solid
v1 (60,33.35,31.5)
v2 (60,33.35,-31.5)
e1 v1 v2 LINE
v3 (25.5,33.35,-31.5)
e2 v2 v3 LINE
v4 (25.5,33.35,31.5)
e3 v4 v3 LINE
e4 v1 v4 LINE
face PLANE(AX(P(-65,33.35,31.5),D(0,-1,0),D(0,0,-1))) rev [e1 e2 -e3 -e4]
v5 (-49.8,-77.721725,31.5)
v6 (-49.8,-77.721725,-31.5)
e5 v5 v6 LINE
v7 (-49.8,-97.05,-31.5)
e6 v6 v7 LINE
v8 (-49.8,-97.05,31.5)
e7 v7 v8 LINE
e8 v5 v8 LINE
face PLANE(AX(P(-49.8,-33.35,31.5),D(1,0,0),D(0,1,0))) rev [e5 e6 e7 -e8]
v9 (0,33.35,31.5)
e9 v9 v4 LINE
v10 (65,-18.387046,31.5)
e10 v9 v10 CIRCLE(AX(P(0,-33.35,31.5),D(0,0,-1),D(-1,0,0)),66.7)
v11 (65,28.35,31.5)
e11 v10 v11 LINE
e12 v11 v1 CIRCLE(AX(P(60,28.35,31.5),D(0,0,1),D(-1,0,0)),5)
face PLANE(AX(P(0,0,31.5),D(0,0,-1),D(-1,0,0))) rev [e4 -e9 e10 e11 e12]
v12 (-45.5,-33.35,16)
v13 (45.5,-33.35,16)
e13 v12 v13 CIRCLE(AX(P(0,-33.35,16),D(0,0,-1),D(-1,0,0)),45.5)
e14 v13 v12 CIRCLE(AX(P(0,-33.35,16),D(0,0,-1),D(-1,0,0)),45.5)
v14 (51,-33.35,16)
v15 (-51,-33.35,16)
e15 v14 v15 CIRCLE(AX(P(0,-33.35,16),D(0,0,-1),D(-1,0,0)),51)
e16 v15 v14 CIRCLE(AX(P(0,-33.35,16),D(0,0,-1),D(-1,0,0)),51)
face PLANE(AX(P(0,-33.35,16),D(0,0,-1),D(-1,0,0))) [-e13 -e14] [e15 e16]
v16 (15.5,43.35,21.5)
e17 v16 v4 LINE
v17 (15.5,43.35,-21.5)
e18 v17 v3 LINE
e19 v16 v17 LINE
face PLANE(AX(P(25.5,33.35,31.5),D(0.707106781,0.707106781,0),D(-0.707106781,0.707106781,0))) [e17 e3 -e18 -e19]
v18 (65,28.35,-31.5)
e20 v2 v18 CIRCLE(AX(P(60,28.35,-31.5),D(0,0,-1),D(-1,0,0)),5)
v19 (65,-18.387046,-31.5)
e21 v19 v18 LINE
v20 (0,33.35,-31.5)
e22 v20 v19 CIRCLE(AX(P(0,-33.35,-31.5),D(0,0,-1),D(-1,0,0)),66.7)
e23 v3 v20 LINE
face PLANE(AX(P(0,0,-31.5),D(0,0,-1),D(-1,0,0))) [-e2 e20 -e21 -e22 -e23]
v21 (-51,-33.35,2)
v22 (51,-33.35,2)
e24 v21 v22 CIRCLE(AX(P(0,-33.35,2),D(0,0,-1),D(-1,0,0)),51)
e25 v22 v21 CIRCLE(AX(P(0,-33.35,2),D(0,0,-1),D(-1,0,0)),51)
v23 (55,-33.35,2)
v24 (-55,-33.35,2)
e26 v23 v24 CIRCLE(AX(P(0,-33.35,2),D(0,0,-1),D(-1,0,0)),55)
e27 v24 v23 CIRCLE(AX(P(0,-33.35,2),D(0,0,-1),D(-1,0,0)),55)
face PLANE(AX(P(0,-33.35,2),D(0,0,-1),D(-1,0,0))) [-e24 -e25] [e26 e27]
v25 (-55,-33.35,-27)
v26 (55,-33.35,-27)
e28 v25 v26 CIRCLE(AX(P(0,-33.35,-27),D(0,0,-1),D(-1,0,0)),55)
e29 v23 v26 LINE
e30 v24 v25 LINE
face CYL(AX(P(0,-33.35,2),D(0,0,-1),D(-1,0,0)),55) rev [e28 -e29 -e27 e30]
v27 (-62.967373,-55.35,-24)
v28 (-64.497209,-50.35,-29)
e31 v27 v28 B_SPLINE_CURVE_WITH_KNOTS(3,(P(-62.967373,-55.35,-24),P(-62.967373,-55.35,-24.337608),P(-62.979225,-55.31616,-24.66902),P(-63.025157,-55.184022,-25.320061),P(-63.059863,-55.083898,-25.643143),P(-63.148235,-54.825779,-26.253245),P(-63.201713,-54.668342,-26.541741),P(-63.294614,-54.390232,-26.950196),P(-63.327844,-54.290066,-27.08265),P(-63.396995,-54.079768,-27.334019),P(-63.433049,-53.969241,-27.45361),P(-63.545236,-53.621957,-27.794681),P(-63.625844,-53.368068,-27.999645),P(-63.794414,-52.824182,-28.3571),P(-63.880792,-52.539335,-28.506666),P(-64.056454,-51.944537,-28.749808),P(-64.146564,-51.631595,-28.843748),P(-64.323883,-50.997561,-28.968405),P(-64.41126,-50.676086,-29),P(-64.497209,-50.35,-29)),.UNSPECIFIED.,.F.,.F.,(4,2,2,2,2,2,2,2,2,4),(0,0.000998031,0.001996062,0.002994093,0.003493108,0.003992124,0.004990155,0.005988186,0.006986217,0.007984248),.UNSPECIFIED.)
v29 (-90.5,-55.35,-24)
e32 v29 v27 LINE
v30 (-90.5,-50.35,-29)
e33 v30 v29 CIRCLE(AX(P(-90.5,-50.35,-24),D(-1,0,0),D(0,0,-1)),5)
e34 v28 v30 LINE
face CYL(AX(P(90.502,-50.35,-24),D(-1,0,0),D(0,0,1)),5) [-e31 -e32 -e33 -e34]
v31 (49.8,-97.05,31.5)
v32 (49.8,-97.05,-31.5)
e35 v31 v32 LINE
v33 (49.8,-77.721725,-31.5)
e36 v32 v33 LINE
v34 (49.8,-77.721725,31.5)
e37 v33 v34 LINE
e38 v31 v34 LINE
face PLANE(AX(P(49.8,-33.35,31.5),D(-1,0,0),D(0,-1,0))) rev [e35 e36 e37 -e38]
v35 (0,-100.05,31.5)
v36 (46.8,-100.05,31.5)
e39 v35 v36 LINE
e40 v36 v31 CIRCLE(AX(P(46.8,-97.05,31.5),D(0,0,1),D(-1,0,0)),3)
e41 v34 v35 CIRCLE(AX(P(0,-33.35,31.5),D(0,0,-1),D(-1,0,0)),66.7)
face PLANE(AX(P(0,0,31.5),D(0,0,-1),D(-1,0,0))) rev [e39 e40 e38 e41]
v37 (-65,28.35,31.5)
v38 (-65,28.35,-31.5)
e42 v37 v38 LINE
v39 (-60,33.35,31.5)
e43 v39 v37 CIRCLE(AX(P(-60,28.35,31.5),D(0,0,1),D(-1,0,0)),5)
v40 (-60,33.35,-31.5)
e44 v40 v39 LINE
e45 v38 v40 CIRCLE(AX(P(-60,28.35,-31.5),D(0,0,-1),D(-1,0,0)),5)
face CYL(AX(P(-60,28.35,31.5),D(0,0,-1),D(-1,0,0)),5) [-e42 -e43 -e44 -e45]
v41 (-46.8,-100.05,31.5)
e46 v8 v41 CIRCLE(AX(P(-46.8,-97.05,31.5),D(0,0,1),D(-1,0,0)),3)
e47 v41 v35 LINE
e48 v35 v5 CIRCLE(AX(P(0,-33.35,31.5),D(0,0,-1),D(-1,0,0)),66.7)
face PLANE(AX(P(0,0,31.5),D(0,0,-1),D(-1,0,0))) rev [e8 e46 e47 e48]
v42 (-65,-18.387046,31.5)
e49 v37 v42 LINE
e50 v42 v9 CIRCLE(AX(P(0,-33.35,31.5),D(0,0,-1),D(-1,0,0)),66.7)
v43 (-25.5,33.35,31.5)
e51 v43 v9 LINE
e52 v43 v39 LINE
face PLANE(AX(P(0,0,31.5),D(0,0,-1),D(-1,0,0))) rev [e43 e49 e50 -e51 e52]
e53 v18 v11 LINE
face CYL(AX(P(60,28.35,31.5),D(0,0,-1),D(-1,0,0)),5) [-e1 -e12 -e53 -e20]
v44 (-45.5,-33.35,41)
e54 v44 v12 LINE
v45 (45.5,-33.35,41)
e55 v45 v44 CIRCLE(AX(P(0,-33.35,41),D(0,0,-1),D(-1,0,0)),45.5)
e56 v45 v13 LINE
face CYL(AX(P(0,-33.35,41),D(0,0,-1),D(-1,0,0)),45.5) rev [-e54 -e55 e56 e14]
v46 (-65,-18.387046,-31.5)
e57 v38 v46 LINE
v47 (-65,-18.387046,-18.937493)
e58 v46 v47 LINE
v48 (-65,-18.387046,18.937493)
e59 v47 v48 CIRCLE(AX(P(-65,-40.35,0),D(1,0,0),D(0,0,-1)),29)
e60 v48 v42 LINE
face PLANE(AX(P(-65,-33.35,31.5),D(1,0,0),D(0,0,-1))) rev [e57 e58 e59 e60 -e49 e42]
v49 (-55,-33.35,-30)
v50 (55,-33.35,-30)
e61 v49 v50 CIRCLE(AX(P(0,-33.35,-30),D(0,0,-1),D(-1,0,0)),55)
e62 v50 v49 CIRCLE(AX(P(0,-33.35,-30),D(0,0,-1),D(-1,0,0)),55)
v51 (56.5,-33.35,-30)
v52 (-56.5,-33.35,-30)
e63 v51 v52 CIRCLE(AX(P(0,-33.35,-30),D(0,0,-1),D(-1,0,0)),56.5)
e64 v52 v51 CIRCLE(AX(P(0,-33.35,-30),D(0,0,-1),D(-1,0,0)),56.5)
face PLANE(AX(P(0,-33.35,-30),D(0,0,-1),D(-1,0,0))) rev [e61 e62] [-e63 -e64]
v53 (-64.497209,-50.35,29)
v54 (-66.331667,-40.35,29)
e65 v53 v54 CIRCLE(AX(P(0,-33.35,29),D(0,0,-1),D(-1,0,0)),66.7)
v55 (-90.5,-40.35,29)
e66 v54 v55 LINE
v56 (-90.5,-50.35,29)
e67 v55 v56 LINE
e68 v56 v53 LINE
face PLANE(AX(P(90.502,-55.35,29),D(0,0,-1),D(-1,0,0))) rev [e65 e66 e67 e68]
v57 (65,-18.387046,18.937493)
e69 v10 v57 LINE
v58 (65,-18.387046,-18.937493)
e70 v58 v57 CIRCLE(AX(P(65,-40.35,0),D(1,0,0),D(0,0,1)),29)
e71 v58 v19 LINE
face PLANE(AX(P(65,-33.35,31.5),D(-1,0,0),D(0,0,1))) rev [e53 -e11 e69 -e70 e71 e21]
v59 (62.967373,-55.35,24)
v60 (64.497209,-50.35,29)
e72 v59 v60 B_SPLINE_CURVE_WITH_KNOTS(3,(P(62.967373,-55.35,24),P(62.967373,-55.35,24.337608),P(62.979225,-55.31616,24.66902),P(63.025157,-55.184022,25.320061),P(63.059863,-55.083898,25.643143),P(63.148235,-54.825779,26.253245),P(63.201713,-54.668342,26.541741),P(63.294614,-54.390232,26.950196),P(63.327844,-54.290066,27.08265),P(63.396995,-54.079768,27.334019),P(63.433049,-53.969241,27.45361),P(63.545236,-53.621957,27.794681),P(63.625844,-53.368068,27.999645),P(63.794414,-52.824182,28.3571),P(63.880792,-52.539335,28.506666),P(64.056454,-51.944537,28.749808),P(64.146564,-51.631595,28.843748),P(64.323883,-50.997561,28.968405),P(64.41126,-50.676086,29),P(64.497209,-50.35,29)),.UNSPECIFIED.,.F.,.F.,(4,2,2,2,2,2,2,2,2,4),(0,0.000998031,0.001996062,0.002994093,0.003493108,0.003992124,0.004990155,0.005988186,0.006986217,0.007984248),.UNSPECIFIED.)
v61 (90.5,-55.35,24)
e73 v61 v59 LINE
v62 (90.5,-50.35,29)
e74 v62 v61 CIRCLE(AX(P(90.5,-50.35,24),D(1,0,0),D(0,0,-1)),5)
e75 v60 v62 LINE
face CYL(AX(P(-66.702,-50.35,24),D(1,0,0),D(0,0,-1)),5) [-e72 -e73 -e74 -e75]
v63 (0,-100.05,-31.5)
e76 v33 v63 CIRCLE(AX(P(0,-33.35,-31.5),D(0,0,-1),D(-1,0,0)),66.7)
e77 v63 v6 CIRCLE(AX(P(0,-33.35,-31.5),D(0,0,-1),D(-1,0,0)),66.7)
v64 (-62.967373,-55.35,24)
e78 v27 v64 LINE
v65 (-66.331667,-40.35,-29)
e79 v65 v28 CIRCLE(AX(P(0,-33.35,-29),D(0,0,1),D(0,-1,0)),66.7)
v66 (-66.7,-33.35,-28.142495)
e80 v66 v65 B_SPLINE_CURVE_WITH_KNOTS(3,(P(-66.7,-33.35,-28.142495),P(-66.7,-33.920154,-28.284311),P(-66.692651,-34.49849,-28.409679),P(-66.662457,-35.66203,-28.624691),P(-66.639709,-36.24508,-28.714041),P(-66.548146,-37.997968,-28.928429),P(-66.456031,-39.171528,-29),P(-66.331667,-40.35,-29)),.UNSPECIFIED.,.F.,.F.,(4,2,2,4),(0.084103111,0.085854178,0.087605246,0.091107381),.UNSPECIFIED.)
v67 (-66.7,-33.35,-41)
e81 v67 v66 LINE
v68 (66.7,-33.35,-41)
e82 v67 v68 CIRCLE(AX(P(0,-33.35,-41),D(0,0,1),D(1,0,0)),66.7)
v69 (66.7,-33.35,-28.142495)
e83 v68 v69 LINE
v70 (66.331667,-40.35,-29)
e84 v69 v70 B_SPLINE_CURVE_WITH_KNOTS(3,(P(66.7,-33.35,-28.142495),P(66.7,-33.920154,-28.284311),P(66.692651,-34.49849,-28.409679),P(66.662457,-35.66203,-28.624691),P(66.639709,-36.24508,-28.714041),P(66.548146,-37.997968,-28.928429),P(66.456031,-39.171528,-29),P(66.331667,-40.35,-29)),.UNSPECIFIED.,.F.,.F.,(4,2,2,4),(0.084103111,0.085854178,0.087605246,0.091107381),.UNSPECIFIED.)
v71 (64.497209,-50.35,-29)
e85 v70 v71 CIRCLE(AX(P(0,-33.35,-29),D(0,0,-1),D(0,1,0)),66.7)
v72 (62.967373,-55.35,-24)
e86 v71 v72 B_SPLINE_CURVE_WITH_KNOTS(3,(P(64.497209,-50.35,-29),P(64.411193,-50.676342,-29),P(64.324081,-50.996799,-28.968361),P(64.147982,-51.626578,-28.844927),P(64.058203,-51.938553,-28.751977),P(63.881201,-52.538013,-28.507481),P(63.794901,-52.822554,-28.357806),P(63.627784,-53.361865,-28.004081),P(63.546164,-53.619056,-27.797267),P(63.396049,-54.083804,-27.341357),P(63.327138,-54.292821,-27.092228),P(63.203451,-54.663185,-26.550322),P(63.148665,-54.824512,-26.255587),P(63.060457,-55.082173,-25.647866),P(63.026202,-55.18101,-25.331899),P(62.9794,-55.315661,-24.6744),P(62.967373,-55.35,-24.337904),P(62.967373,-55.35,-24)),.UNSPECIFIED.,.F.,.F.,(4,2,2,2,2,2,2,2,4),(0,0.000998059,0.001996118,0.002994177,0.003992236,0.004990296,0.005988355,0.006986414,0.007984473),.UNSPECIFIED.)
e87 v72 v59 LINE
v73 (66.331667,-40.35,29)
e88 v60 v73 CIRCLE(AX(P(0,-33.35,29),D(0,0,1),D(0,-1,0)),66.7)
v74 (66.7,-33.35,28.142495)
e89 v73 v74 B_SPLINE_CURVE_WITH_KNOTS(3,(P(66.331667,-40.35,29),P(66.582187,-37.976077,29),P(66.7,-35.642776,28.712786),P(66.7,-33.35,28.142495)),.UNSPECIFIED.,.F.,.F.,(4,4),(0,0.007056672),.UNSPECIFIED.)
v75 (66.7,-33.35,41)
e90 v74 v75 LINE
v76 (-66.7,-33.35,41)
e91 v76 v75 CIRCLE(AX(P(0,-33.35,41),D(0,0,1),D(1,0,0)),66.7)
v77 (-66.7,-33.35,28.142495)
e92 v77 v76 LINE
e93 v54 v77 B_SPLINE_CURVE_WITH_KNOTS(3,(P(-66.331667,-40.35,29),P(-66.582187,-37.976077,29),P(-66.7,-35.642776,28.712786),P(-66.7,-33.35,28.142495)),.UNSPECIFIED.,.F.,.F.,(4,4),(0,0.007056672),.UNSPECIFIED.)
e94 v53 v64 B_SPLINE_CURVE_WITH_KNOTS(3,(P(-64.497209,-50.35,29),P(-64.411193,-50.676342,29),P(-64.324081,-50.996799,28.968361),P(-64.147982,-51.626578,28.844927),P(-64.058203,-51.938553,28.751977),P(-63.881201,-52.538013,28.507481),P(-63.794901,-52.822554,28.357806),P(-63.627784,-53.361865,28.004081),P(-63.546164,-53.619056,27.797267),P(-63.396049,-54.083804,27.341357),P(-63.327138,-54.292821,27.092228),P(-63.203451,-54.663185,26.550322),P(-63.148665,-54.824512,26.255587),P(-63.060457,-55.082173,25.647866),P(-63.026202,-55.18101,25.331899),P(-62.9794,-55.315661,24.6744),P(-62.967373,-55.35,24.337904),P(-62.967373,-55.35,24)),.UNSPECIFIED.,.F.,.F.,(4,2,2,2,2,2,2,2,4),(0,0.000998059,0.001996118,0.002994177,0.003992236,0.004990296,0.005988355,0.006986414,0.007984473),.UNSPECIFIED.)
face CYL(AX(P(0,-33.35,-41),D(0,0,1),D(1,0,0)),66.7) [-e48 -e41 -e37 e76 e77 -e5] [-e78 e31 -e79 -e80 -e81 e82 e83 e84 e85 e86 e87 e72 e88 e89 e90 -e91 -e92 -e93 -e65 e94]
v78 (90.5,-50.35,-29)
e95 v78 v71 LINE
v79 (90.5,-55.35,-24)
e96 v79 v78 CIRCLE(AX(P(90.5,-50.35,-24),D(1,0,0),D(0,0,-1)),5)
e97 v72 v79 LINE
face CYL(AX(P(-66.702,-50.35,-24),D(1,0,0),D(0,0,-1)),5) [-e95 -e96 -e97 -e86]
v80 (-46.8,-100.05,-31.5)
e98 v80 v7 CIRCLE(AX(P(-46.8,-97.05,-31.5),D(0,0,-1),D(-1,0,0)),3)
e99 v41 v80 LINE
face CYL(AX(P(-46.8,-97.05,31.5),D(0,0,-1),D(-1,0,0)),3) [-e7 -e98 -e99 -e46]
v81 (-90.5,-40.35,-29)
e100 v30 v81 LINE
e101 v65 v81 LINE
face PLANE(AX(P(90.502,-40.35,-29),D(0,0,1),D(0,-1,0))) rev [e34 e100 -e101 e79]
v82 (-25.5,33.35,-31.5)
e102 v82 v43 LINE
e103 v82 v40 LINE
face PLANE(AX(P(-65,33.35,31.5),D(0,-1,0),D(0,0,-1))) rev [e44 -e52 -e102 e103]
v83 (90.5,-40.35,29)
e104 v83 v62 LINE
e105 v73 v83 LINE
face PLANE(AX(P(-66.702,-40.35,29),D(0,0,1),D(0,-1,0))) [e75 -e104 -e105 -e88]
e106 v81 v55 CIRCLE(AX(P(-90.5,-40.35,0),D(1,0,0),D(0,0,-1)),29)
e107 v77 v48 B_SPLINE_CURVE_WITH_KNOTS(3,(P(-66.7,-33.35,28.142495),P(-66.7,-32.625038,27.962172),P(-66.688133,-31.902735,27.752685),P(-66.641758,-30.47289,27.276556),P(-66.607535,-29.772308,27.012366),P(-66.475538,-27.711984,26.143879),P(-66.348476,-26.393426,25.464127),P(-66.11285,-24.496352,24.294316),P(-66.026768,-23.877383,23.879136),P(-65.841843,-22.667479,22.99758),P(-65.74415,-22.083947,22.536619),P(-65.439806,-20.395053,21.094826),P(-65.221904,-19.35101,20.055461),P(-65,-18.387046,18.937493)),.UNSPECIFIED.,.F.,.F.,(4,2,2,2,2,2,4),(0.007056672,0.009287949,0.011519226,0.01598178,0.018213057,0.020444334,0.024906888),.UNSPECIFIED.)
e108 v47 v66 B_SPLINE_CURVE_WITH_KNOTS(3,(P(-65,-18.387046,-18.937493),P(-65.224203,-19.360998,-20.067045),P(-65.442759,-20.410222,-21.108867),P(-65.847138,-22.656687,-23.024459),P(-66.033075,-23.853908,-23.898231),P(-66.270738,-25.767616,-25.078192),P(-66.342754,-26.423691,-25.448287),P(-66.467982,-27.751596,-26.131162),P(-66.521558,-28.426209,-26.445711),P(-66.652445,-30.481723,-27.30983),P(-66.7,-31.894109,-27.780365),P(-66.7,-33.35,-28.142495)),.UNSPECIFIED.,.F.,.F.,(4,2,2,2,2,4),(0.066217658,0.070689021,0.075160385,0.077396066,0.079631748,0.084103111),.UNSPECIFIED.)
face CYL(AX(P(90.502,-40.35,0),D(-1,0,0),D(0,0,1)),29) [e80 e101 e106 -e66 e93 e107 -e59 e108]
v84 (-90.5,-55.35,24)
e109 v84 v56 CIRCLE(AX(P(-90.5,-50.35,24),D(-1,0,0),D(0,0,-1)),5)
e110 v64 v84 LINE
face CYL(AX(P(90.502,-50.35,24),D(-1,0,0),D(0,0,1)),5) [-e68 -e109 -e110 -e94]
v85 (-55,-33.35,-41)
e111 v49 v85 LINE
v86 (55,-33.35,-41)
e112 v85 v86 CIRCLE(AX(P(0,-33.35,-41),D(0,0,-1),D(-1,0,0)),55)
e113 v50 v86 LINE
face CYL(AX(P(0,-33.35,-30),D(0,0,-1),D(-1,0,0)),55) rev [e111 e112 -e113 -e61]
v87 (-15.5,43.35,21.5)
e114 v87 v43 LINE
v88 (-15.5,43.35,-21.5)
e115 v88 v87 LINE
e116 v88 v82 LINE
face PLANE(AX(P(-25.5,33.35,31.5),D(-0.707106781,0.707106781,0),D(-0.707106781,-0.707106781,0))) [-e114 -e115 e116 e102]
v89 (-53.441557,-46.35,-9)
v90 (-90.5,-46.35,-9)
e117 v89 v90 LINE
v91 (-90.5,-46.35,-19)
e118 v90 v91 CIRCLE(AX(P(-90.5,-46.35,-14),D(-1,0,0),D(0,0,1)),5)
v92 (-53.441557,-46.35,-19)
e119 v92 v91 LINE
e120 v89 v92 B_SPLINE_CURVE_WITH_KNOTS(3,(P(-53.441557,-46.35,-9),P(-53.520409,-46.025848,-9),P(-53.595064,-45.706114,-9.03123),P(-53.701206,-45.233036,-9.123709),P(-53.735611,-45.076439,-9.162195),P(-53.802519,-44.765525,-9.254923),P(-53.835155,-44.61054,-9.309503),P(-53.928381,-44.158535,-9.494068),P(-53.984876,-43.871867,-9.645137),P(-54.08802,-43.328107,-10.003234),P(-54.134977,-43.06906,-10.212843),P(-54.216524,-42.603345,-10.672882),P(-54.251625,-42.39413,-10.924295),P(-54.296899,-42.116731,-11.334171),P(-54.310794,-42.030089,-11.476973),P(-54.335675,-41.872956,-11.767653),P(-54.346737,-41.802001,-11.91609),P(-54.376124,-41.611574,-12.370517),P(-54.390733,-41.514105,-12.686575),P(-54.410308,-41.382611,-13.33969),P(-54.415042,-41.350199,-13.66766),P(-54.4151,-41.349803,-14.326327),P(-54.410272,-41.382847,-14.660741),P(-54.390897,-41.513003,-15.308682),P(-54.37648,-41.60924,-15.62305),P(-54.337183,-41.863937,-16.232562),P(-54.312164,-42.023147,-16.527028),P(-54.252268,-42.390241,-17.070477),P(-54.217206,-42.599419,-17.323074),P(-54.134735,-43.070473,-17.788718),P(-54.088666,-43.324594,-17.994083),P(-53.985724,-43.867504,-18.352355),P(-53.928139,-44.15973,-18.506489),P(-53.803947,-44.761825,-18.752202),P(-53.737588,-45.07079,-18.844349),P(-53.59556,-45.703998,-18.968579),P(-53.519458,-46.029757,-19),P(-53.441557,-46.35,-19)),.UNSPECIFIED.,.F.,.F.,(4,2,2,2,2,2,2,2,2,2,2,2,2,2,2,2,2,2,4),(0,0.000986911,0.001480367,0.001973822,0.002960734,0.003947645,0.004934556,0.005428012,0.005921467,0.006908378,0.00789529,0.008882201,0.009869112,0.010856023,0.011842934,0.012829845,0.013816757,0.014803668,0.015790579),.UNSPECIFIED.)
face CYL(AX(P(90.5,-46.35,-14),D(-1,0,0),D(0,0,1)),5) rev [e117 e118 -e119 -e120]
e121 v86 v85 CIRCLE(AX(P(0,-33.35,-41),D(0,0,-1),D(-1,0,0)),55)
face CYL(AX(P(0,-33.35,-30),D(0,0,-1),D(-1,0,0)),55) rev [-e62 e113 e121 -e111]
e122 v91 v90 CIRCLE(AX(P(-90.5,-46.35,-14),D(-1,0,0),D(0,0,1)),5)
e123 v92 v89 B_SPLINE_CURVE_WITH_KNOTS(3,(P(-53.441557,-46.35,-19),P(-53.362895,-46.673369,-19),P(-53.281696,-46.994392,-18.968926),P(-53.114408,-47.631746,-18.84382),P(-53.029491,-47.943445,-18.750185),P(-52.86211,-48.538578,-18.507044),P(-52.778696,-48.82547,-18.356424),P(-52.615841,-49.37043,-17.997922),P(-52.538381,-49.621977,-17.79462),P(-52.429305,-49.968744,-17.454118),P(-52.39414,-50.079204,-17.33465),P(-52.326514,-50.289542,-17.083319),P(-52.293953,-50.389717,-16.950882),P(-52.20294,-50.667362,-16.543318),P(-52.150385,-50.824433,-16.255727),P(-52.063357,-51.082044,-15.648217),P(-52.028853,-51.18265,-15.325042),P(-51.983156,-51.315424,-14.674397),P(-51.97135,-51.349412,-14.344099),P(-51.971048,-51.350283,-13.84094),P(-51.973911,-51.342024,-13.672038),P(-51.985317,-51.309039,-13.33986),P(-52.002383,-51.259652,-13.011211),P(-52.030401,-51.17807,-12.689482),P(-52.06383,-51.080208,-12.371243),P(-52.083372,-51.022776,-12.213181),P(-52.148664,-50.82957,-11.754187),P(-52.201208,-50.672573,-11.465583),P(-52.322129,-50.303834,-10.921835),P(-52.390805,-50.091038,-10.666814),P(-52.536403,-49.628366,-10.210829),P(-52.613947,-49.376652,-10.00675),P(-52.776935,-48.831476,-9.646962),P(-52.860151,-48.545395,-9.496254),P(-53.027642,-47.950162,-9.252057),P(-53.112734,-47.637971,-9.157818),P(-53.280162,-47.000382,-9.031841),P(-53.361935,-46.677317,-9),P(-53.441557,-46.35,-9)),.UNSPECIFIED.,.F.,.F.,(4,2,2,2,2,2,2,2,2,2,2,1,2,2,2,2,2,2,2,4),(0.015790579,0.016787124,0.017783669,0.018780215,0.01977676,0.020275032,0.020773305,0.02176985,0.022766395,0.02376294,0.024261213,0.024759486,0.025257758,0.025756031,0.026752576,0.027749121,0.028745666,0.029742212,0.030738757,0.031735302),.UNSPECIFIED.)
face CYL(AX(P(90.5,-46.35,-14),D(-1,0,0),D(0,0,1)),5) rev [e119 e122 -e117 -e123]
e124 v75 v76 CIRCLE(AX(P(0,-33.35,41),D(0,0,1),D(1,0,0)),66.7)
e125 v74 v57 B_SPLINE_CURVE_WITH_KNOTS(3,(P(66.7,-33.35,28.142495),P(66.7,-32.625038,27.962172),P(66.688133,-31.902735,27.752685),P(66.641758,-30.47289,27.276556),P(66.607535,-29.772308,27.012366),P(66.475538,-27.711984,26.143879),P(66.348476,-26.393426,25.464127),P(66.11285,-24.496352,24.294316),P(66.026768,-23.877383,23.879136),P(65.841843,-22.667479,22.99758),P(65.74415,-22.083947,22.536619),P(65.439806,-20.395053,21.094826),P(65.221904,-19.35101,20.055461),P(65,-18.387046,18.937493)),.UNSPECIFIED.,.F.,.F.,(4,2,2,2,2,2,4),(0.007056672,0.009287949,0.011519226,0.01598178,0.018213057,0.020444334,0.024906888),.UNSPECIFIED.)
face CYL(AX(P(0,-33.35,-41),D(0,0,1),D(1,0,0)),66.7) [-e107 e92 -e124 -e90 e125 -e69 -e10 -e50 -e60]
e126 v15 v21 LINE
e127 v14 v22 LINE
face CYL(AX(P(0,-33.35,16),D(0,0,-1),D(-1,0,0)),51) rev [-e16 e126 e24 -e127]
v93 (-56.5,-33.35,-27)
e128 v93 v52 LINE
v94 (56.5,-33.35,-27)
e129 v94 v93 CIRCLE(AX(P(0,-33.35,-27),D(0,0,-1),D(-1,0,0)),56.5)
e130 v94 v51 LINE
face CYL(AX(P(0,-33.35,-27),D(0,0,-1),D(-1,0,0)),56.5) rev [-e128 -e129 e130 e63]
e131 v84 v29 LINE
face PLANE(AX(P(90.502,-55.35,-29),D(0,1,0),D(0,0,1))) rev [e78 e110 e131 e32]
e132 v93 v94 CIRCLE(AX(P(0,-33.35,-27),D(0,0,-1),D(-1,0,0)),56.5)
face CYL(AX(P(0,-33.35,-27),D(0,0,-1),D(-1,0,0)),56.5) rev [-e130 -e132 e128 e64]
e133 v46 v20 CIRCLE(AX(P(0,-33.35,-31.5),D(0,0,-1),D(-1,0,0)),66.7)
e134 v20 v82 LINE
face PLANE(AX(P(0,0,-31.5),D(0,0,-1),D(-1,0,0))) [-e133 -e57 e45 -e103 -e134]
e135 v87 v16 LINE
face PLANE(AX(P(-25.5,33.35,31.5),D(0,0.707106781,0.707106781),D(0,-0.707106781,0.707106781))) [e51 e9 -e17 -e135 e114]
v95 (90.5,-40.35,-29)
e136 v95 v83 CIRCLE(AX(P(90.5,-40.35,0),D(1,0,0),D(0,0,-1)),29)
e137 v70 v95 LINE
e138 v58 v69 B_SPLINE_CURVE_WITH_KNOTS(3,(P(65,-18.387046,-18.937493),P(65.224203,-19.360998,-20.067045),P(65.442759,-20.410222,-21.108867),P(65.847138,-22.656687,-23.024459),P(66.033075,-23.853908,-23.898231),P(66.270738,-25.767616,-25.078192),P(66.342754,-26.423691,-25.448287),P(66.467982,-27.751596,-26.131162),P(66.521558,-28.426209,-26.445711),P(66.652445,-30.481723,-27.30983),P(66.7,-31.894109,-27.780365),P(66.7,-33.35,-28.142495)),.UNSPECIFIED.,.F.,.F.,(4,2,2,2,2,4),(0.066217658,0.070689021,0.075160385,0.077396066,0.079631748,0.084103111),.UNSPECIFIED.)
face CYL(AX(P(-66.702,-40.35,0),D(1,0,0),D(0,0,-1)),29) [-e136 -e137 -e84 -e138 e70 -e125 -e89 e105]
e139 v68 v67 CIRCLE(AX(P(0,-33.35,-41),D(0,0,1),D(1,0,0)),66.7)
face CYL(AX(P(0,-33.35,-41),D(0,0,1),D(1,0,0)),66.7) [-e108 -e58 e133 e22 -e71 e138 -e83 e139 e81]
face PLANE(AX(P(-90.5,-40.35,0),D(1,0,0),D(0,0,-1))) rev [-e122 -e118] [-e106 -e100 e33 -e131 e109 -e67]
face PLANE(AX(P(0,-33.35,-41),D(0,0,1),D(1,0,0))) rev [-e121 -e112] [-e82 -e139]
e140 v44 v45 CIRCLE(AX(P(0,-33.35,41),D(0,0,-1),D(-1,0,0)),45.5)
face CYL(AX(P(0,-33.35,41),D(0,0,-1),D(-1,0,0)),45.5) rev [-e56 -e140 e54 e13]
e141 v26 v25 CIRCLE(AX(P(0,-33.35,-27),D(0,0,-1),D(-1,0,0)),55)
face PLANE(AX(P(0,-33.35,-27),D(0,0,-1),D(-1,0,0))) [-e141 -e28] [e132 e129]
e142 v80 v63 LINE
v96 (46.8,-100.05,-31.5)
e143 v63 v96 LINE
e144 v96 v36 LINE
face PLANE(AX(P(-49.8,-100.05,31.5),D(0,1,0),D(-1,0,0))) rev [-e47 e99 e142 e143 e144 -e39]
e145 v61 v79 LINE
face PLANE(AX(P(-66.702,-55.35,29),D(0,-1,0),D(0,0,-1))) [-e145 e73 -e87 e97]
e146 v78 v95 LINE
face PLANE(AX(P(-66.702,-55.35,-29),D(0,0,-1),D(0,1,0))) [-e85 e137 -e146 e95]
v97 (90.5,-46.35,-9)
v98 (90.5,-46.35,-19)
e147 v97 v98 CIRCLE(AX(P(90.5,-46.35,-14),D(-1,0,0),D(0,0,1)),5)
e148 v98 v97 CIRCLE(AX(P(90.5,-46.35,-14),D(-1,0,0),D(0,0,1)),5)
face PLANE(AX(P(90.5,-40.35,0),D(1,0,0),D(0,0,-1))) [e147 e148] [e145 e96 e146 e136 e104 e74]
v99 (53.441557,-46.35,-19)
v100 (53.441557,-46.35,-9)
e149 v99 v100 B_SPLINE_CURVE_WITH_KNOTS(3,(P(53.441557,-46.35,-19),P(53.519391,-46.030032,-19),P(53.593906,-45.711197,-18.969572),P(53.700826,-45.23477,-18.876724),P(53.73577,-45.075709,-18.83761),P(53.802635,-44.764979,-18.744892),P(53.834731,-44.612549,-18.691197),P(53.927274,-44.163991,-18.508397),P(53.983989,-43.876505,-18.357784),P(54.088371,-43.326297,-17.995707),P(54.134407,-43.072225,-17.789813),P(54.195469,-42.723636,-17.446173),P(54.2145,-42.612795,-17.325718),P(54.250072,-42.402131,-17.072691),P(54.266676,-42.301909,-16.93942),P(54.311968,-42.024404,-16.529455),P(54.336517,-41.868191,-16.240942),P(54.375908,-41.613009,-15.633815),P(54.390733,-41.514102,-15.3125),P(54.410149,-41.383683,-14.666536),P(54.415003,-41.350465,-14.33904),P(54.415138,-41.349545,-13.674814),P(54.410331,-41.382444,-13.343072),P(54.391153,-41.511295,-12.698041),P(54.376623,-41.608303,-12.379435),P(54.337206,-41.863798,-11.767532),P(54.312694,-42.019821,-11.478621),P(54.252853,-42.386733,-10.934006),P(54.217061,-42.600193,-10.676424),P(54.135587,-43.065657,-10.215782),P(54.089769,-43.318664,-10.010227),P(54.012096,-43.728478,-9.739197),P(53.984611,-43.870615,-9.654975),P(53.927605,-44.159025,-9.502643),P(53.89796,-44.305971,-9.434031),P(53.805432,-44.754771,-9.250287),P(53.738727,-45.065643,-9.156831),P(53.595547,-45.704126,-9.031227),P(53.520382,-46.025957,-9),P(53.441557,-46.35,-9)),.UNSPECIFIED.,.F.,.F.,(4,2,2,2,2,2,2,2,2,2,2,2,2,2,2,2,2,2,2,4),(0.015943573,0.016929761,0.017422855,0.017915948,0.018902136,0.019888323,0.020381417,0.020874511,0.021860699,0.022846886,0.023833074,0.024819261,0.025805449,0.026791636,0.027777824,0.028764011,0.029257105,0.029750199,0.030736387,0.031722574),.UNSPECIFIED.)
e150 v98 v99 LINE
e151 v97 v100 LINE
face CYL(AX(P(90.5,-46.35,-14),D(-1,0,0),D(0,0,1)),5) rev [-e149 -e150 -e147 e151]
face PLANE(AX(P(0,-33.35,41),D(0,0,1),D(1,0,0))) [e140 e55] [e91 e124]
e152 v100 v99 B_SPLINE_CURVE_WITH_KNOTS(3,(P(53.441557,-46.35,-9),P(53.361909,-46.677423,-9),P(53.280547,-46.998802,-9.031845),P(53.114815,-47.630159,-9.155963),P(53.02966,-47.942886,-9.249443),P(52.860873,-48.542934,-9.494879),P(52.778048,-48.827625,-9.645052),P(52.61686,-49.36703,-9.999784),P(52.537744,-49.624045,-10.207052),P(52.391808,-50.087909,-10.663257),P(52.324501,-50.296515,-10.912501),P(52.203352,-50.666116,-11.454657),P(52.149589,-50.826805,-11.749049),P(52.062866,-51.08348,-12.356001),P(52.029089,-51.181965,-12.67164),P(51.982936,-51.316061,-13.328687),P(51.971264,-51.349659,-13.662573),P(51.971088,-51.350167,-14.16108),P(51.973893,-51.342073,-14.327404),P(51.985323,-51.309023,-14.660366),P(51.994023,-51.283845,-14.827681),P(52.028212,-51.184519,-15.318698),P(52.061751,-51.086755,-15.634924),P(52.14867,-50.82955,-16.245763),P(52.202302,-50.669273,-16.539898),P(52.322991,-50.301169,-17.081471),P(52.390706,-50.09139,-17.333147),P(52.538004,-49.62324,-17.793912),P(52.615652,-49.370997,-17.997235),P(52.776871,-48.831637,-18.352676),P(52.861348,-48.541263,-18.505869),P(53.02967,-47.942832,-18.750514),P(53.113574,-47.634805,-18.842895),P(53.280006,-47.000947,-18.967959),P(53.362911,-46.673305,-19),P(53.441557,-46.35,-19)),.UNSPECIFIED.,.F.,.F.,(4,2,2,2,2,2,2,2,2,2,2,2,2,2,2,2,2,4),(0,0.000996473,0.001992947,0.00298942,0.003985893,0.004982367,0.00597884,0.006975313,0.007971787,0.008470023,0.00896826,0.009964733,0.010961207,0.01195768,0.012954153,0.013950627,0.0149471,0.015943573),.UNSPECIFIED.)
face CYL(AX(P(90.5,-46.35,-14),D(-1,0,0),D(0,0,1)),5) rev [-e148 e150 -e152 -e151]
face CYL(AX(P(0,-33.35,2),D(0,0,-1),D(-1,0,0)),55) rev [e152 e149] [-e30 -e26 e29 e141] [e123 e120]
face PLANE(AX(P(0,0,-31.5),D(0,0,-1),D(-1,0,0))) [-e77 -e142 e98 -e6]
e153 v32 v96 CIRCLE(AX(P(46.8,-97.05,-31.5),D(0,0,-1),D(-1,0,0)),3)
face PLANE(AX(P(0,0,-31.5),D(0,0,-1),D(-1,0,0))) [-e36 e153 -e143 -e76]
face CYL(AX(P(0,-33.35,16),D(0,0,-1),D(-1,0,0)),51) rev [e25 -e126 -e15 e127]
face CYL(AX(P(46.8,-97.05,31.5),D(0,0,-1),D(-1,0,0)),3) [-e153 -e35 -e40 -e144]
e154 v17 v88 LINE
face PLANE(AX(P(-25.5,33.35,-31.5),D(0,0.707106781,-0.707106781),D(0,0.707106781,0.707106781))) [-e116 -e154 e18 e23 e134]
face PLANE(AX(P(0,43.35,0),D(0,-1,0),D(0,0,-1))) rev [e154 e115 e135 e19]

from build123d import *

# Parameters (mm, degrees)
BASE_BLOCK_SKETCH_W           = 130
BASE_BLOCK_SKETCH_H           = 66.7
BASE_BLOCK_130X63_DEPTH       = 31.5
TOP_BOSS_SKETCH_W             = 51
TOP_BOSS_SKETCH_H             = 63
TOP_BOSS_DRAFTED_45DEG_DEPTH  = 10
TOP_BOSS_DRAFTED_45DEG_TAPER  = 45
UPPER_BLOCK_SKETCH_W          = 99.6
UPPER_BLOCK_SKETCH_H          = 66.7
UPPER_BLOCK_99_6X63_DEPTH     = 31.5
BARREL_START                  = 9.5
BARREL_SKETCH_133_4_R         = 66.7
BARREL_133_4_THIN_WALL_DEPTH  = 82
FRONT_BORE_SKETCH_110_R       = 55
FRONT_BORE_110_DEPTH          = 11
SNAP_RING_GROOVE_SKETCH_113_R = 56.5
SNAP_RING_GROOVE_113_DEPTH    = 3
BEARING_SEAT_SKETCH_110_R     = 55
BEARING_SEAT_110_DEPTH        = 29
STEP_BORE_SKETCH_102_R        = 51
STEP_BORE_102_DEPTH           = 14
THROUGH_BORE_SKETCH_91_R      = 45.5
THROUGH_BORE_91_DEPTH         = 25
SIDE_LUG_1_REACH              = 192.795
SIDE_LUG_2_REACH              = 212.836
LUG_HOLE_SKETCH_R             = 5
LUG_HOLE_DEPTH                = 211.836435571
LUG_FILLETS_R5_R              = 5
UPPER_BLOCK_FILLETS_R3_R      = 3


with BuildPart() as part:
    # Base Block Sketch → Base Block 130x63 (new, symmetric)
    with BuildSketch(Plane.XY):
        Rectangle(BASE_BLOCK_SKETCH_W, BASE_BLOCK_SKETCH_H)
    extrude(amount=BASE_BLOCK_130X63_DEPTH, both=True)

    # Top Boss Sketch → Top Boss Drafted 45deg (add)
    with BuildSketch(Plane(origin=(0, 33.35, 0), x_dir=(1, 0, 0), z_dir=(0, 1, 0))):
        Rectangle(TOP_BOSS_SKETCH_W, TOP_BOSS_SKETCH_H)
    extrude(amount=TOP_BOSS_DRAFTED_45DEG_DEPTH, taper=TOP_BOSS_DRAFTED_45DEG_TAPER)

    # Upper Block Sketch → Upper Block 99.6x63 (add, symmetric)
    with BuildSketch(Plane.XY):
        with Locations((0, -66.7)):
            Rectangle(UPPER_BLOCK_SKETCH_W, UPPER_BLOCK_SKETCH_H)
    extrude(amount=UPPER_BLOCK_99_6X63_DEPTH, both=True)

    # Barrel Sketch Ø133.4 → Barrel Ø133.4 Thin Wall (add)
    with BuildSketch(Plane.XY.offset(31.5).offset(BARREL_START)):
        with Locations((0, -33.35)):
            Circle(BARREL_SKETCH_133_4_R)
    extrude(amount=-BARREL_133_4_THIN_WALL_DEPTH)

    # Front Bore Sketch Ø110 → Front Bore Ø110 (cut)
    with BuildSketch(Plane(origin=(0, 0, -41), x_dir=(-1, 0, 0), z_dir=(0, 0, -1))):
        with Locations((0, -33.35)):
            Circle(FRONT_BORE_SKETCH_110_R)
    extrude(amount=-FRONT_BORE_110_DEPTH, mode=Mode.SUBTRACT)

    # Snap Ring Groove Sketch Ø113 → Snap Ring Groove Ø113 (cut)
    with BuildSketch(Plane(origin=(0, 0, -30), x_dir=(-1, 0, 0), z_dir=(0, 0, -1))):
        with Locations((0, -33.35)):
            Circle(SNAP_RING_GROOVE_SKETCH_113_R)
    extrude(amount=-SNAP_RING_GROOVE_113_DEPTH, mode=Mode.SUBTRACT)

    # Bearing Seat Sketch Ø110 → Bearing Seat Ø110 (cut)
    with BuildSketch(Plane(origin=(0, 0, -27), x_dir=(-1, 0, 0), z_dir=(0, 0, -1))):
        with Locations((0, -33.35)):
            Circle(BEARING_SEAT_SKETCH_110_R)
    extrude(amount=-BEARING_SEAT_110_DEPTH, mode=Mode.SUBTRACT)

    # Step Bore Sketch Ø102 → Step Bore Ø102 (cut)
    with BuildSketch(Plane(origin=(0, 0, 2), x_dir=(-1, 0, 0), z_dir=(0, 0, -1))):
        with Locations((0, -33.35)):
            Circle(STEP_BORE_SKETCH_102_R)
    extrude(amount=-STEP_BORE_102_DEPTH, mode=Mode.SUBTRACT)

    # Through Bore Sketch Ø91 → Through Bore Ø91 (cut)
    with BuildSketch(Plane(origin=(0, 0, 16), x_dir=(-1, 0, 0), z_dir=(0, 0, -1))):
        with Locations((0, -33.35)):
            Circle(THROUGH_BORE_SKETCH_91_R)
    extrude(amount=-THROUGH_BORE_91_DEPTH, mode=Mode.SUBTRACT)

    # Side Lug 1 Sketch → Side Lug 1 (add, up to next)
    with BuildSketch(Plane(origin=(90.5, 0, 0), x_dir=(0, 0, -1), z_dir=(1, 0, 0)), mode=Mode.PRIVATE) as side_lug_1_sk1:
        with BuildLine():
            Line((-29, -40.35), (-29, -55.35))
            Line((-29, -55.35), (29, -55.35))
            Line((29, -55.35), (29, -40.35))
            ThreePointArc((29, -40.35), (0, -11.35), (-29, -40.35))
        make_face()
    side_lug_1_tool1 = extrude(side_lug_1_sk1.sketch, amount=-SIDE_LUG_1_REACH, mode=Mode.PRIVATE) - part.part
    add(side_lug_1_tool1.solids().sort_by_distance((90.5, -35.907208, 0))[0])

    # Side Lug 2 Sketch → Side Lug 2 (add, up to next)
    with BuildSketch(Plane(origin=(-90.5, 0, 0), x_dir=(0, 0, -1), z_dir=(1, 0, 0)), mode=Mode.PRIVATE) as side_lug_2_sk1:
        with BuildLine():
            Line((29, -55.35), (-29, -55.35))
            Line((-29, -55.35), (-29, -40.35))
            ThreePointArc((-29, -40.35), (0, -11.35), (29, -40.35))
            Line((29, -40.35), (29, -55.35))
        make_face()
    side_lug_2_tool1 = extrude(side_lug_2_sk1.sketch, amount=SIDE_LUG_2_REACH, mode=Mode.PRIVATE) - part.part
    add(side_lug_2_tool1.solids().sort_by_distance((-90.5, -35.907208, 0))[0])

    # Lug Hole Sketch → Lug Hole (cut, through all)
    with BuildSketch(Plane.ZY.offset(90.5)):
        with Locations((-14, -46.35)):
            Circle(LUG_HOLE_SKETCH_R)
    extrude(amount=-LUG_HOLE_DEPTH, mode=Mode.SUBTRACT)

    # Lug Fillets R5
    lug_fillets_r5_edges = [part.edges().sort_by_distance(p)[0] for p in [
        (-76.733686252, -55.35, 29),
        (-76.733686252, -55.35, -29),
        (-65, 33.35, 0),
        (65, 33.35, 0),
        (76.733686252, -55.35, 29),
        (76.733686252, -55.35, -29),
    ]]
    fillet(lug_fillets_r5_edges, radius=LUG_FILLETS_R5_R)

    # Upper Block Fillets R3
    upper_block_fillets_r3_edges = [part.edges().sort_by_distance(p)[0] for p in [
        (-49.8, -100.05, 0),
        (49.8, -100.05, 0),
    ]]
    fillet(upper_block_fillets_r3_edges, radius=UPPER_BLOCK_FILLETS_R3_R)


solid = part.part
